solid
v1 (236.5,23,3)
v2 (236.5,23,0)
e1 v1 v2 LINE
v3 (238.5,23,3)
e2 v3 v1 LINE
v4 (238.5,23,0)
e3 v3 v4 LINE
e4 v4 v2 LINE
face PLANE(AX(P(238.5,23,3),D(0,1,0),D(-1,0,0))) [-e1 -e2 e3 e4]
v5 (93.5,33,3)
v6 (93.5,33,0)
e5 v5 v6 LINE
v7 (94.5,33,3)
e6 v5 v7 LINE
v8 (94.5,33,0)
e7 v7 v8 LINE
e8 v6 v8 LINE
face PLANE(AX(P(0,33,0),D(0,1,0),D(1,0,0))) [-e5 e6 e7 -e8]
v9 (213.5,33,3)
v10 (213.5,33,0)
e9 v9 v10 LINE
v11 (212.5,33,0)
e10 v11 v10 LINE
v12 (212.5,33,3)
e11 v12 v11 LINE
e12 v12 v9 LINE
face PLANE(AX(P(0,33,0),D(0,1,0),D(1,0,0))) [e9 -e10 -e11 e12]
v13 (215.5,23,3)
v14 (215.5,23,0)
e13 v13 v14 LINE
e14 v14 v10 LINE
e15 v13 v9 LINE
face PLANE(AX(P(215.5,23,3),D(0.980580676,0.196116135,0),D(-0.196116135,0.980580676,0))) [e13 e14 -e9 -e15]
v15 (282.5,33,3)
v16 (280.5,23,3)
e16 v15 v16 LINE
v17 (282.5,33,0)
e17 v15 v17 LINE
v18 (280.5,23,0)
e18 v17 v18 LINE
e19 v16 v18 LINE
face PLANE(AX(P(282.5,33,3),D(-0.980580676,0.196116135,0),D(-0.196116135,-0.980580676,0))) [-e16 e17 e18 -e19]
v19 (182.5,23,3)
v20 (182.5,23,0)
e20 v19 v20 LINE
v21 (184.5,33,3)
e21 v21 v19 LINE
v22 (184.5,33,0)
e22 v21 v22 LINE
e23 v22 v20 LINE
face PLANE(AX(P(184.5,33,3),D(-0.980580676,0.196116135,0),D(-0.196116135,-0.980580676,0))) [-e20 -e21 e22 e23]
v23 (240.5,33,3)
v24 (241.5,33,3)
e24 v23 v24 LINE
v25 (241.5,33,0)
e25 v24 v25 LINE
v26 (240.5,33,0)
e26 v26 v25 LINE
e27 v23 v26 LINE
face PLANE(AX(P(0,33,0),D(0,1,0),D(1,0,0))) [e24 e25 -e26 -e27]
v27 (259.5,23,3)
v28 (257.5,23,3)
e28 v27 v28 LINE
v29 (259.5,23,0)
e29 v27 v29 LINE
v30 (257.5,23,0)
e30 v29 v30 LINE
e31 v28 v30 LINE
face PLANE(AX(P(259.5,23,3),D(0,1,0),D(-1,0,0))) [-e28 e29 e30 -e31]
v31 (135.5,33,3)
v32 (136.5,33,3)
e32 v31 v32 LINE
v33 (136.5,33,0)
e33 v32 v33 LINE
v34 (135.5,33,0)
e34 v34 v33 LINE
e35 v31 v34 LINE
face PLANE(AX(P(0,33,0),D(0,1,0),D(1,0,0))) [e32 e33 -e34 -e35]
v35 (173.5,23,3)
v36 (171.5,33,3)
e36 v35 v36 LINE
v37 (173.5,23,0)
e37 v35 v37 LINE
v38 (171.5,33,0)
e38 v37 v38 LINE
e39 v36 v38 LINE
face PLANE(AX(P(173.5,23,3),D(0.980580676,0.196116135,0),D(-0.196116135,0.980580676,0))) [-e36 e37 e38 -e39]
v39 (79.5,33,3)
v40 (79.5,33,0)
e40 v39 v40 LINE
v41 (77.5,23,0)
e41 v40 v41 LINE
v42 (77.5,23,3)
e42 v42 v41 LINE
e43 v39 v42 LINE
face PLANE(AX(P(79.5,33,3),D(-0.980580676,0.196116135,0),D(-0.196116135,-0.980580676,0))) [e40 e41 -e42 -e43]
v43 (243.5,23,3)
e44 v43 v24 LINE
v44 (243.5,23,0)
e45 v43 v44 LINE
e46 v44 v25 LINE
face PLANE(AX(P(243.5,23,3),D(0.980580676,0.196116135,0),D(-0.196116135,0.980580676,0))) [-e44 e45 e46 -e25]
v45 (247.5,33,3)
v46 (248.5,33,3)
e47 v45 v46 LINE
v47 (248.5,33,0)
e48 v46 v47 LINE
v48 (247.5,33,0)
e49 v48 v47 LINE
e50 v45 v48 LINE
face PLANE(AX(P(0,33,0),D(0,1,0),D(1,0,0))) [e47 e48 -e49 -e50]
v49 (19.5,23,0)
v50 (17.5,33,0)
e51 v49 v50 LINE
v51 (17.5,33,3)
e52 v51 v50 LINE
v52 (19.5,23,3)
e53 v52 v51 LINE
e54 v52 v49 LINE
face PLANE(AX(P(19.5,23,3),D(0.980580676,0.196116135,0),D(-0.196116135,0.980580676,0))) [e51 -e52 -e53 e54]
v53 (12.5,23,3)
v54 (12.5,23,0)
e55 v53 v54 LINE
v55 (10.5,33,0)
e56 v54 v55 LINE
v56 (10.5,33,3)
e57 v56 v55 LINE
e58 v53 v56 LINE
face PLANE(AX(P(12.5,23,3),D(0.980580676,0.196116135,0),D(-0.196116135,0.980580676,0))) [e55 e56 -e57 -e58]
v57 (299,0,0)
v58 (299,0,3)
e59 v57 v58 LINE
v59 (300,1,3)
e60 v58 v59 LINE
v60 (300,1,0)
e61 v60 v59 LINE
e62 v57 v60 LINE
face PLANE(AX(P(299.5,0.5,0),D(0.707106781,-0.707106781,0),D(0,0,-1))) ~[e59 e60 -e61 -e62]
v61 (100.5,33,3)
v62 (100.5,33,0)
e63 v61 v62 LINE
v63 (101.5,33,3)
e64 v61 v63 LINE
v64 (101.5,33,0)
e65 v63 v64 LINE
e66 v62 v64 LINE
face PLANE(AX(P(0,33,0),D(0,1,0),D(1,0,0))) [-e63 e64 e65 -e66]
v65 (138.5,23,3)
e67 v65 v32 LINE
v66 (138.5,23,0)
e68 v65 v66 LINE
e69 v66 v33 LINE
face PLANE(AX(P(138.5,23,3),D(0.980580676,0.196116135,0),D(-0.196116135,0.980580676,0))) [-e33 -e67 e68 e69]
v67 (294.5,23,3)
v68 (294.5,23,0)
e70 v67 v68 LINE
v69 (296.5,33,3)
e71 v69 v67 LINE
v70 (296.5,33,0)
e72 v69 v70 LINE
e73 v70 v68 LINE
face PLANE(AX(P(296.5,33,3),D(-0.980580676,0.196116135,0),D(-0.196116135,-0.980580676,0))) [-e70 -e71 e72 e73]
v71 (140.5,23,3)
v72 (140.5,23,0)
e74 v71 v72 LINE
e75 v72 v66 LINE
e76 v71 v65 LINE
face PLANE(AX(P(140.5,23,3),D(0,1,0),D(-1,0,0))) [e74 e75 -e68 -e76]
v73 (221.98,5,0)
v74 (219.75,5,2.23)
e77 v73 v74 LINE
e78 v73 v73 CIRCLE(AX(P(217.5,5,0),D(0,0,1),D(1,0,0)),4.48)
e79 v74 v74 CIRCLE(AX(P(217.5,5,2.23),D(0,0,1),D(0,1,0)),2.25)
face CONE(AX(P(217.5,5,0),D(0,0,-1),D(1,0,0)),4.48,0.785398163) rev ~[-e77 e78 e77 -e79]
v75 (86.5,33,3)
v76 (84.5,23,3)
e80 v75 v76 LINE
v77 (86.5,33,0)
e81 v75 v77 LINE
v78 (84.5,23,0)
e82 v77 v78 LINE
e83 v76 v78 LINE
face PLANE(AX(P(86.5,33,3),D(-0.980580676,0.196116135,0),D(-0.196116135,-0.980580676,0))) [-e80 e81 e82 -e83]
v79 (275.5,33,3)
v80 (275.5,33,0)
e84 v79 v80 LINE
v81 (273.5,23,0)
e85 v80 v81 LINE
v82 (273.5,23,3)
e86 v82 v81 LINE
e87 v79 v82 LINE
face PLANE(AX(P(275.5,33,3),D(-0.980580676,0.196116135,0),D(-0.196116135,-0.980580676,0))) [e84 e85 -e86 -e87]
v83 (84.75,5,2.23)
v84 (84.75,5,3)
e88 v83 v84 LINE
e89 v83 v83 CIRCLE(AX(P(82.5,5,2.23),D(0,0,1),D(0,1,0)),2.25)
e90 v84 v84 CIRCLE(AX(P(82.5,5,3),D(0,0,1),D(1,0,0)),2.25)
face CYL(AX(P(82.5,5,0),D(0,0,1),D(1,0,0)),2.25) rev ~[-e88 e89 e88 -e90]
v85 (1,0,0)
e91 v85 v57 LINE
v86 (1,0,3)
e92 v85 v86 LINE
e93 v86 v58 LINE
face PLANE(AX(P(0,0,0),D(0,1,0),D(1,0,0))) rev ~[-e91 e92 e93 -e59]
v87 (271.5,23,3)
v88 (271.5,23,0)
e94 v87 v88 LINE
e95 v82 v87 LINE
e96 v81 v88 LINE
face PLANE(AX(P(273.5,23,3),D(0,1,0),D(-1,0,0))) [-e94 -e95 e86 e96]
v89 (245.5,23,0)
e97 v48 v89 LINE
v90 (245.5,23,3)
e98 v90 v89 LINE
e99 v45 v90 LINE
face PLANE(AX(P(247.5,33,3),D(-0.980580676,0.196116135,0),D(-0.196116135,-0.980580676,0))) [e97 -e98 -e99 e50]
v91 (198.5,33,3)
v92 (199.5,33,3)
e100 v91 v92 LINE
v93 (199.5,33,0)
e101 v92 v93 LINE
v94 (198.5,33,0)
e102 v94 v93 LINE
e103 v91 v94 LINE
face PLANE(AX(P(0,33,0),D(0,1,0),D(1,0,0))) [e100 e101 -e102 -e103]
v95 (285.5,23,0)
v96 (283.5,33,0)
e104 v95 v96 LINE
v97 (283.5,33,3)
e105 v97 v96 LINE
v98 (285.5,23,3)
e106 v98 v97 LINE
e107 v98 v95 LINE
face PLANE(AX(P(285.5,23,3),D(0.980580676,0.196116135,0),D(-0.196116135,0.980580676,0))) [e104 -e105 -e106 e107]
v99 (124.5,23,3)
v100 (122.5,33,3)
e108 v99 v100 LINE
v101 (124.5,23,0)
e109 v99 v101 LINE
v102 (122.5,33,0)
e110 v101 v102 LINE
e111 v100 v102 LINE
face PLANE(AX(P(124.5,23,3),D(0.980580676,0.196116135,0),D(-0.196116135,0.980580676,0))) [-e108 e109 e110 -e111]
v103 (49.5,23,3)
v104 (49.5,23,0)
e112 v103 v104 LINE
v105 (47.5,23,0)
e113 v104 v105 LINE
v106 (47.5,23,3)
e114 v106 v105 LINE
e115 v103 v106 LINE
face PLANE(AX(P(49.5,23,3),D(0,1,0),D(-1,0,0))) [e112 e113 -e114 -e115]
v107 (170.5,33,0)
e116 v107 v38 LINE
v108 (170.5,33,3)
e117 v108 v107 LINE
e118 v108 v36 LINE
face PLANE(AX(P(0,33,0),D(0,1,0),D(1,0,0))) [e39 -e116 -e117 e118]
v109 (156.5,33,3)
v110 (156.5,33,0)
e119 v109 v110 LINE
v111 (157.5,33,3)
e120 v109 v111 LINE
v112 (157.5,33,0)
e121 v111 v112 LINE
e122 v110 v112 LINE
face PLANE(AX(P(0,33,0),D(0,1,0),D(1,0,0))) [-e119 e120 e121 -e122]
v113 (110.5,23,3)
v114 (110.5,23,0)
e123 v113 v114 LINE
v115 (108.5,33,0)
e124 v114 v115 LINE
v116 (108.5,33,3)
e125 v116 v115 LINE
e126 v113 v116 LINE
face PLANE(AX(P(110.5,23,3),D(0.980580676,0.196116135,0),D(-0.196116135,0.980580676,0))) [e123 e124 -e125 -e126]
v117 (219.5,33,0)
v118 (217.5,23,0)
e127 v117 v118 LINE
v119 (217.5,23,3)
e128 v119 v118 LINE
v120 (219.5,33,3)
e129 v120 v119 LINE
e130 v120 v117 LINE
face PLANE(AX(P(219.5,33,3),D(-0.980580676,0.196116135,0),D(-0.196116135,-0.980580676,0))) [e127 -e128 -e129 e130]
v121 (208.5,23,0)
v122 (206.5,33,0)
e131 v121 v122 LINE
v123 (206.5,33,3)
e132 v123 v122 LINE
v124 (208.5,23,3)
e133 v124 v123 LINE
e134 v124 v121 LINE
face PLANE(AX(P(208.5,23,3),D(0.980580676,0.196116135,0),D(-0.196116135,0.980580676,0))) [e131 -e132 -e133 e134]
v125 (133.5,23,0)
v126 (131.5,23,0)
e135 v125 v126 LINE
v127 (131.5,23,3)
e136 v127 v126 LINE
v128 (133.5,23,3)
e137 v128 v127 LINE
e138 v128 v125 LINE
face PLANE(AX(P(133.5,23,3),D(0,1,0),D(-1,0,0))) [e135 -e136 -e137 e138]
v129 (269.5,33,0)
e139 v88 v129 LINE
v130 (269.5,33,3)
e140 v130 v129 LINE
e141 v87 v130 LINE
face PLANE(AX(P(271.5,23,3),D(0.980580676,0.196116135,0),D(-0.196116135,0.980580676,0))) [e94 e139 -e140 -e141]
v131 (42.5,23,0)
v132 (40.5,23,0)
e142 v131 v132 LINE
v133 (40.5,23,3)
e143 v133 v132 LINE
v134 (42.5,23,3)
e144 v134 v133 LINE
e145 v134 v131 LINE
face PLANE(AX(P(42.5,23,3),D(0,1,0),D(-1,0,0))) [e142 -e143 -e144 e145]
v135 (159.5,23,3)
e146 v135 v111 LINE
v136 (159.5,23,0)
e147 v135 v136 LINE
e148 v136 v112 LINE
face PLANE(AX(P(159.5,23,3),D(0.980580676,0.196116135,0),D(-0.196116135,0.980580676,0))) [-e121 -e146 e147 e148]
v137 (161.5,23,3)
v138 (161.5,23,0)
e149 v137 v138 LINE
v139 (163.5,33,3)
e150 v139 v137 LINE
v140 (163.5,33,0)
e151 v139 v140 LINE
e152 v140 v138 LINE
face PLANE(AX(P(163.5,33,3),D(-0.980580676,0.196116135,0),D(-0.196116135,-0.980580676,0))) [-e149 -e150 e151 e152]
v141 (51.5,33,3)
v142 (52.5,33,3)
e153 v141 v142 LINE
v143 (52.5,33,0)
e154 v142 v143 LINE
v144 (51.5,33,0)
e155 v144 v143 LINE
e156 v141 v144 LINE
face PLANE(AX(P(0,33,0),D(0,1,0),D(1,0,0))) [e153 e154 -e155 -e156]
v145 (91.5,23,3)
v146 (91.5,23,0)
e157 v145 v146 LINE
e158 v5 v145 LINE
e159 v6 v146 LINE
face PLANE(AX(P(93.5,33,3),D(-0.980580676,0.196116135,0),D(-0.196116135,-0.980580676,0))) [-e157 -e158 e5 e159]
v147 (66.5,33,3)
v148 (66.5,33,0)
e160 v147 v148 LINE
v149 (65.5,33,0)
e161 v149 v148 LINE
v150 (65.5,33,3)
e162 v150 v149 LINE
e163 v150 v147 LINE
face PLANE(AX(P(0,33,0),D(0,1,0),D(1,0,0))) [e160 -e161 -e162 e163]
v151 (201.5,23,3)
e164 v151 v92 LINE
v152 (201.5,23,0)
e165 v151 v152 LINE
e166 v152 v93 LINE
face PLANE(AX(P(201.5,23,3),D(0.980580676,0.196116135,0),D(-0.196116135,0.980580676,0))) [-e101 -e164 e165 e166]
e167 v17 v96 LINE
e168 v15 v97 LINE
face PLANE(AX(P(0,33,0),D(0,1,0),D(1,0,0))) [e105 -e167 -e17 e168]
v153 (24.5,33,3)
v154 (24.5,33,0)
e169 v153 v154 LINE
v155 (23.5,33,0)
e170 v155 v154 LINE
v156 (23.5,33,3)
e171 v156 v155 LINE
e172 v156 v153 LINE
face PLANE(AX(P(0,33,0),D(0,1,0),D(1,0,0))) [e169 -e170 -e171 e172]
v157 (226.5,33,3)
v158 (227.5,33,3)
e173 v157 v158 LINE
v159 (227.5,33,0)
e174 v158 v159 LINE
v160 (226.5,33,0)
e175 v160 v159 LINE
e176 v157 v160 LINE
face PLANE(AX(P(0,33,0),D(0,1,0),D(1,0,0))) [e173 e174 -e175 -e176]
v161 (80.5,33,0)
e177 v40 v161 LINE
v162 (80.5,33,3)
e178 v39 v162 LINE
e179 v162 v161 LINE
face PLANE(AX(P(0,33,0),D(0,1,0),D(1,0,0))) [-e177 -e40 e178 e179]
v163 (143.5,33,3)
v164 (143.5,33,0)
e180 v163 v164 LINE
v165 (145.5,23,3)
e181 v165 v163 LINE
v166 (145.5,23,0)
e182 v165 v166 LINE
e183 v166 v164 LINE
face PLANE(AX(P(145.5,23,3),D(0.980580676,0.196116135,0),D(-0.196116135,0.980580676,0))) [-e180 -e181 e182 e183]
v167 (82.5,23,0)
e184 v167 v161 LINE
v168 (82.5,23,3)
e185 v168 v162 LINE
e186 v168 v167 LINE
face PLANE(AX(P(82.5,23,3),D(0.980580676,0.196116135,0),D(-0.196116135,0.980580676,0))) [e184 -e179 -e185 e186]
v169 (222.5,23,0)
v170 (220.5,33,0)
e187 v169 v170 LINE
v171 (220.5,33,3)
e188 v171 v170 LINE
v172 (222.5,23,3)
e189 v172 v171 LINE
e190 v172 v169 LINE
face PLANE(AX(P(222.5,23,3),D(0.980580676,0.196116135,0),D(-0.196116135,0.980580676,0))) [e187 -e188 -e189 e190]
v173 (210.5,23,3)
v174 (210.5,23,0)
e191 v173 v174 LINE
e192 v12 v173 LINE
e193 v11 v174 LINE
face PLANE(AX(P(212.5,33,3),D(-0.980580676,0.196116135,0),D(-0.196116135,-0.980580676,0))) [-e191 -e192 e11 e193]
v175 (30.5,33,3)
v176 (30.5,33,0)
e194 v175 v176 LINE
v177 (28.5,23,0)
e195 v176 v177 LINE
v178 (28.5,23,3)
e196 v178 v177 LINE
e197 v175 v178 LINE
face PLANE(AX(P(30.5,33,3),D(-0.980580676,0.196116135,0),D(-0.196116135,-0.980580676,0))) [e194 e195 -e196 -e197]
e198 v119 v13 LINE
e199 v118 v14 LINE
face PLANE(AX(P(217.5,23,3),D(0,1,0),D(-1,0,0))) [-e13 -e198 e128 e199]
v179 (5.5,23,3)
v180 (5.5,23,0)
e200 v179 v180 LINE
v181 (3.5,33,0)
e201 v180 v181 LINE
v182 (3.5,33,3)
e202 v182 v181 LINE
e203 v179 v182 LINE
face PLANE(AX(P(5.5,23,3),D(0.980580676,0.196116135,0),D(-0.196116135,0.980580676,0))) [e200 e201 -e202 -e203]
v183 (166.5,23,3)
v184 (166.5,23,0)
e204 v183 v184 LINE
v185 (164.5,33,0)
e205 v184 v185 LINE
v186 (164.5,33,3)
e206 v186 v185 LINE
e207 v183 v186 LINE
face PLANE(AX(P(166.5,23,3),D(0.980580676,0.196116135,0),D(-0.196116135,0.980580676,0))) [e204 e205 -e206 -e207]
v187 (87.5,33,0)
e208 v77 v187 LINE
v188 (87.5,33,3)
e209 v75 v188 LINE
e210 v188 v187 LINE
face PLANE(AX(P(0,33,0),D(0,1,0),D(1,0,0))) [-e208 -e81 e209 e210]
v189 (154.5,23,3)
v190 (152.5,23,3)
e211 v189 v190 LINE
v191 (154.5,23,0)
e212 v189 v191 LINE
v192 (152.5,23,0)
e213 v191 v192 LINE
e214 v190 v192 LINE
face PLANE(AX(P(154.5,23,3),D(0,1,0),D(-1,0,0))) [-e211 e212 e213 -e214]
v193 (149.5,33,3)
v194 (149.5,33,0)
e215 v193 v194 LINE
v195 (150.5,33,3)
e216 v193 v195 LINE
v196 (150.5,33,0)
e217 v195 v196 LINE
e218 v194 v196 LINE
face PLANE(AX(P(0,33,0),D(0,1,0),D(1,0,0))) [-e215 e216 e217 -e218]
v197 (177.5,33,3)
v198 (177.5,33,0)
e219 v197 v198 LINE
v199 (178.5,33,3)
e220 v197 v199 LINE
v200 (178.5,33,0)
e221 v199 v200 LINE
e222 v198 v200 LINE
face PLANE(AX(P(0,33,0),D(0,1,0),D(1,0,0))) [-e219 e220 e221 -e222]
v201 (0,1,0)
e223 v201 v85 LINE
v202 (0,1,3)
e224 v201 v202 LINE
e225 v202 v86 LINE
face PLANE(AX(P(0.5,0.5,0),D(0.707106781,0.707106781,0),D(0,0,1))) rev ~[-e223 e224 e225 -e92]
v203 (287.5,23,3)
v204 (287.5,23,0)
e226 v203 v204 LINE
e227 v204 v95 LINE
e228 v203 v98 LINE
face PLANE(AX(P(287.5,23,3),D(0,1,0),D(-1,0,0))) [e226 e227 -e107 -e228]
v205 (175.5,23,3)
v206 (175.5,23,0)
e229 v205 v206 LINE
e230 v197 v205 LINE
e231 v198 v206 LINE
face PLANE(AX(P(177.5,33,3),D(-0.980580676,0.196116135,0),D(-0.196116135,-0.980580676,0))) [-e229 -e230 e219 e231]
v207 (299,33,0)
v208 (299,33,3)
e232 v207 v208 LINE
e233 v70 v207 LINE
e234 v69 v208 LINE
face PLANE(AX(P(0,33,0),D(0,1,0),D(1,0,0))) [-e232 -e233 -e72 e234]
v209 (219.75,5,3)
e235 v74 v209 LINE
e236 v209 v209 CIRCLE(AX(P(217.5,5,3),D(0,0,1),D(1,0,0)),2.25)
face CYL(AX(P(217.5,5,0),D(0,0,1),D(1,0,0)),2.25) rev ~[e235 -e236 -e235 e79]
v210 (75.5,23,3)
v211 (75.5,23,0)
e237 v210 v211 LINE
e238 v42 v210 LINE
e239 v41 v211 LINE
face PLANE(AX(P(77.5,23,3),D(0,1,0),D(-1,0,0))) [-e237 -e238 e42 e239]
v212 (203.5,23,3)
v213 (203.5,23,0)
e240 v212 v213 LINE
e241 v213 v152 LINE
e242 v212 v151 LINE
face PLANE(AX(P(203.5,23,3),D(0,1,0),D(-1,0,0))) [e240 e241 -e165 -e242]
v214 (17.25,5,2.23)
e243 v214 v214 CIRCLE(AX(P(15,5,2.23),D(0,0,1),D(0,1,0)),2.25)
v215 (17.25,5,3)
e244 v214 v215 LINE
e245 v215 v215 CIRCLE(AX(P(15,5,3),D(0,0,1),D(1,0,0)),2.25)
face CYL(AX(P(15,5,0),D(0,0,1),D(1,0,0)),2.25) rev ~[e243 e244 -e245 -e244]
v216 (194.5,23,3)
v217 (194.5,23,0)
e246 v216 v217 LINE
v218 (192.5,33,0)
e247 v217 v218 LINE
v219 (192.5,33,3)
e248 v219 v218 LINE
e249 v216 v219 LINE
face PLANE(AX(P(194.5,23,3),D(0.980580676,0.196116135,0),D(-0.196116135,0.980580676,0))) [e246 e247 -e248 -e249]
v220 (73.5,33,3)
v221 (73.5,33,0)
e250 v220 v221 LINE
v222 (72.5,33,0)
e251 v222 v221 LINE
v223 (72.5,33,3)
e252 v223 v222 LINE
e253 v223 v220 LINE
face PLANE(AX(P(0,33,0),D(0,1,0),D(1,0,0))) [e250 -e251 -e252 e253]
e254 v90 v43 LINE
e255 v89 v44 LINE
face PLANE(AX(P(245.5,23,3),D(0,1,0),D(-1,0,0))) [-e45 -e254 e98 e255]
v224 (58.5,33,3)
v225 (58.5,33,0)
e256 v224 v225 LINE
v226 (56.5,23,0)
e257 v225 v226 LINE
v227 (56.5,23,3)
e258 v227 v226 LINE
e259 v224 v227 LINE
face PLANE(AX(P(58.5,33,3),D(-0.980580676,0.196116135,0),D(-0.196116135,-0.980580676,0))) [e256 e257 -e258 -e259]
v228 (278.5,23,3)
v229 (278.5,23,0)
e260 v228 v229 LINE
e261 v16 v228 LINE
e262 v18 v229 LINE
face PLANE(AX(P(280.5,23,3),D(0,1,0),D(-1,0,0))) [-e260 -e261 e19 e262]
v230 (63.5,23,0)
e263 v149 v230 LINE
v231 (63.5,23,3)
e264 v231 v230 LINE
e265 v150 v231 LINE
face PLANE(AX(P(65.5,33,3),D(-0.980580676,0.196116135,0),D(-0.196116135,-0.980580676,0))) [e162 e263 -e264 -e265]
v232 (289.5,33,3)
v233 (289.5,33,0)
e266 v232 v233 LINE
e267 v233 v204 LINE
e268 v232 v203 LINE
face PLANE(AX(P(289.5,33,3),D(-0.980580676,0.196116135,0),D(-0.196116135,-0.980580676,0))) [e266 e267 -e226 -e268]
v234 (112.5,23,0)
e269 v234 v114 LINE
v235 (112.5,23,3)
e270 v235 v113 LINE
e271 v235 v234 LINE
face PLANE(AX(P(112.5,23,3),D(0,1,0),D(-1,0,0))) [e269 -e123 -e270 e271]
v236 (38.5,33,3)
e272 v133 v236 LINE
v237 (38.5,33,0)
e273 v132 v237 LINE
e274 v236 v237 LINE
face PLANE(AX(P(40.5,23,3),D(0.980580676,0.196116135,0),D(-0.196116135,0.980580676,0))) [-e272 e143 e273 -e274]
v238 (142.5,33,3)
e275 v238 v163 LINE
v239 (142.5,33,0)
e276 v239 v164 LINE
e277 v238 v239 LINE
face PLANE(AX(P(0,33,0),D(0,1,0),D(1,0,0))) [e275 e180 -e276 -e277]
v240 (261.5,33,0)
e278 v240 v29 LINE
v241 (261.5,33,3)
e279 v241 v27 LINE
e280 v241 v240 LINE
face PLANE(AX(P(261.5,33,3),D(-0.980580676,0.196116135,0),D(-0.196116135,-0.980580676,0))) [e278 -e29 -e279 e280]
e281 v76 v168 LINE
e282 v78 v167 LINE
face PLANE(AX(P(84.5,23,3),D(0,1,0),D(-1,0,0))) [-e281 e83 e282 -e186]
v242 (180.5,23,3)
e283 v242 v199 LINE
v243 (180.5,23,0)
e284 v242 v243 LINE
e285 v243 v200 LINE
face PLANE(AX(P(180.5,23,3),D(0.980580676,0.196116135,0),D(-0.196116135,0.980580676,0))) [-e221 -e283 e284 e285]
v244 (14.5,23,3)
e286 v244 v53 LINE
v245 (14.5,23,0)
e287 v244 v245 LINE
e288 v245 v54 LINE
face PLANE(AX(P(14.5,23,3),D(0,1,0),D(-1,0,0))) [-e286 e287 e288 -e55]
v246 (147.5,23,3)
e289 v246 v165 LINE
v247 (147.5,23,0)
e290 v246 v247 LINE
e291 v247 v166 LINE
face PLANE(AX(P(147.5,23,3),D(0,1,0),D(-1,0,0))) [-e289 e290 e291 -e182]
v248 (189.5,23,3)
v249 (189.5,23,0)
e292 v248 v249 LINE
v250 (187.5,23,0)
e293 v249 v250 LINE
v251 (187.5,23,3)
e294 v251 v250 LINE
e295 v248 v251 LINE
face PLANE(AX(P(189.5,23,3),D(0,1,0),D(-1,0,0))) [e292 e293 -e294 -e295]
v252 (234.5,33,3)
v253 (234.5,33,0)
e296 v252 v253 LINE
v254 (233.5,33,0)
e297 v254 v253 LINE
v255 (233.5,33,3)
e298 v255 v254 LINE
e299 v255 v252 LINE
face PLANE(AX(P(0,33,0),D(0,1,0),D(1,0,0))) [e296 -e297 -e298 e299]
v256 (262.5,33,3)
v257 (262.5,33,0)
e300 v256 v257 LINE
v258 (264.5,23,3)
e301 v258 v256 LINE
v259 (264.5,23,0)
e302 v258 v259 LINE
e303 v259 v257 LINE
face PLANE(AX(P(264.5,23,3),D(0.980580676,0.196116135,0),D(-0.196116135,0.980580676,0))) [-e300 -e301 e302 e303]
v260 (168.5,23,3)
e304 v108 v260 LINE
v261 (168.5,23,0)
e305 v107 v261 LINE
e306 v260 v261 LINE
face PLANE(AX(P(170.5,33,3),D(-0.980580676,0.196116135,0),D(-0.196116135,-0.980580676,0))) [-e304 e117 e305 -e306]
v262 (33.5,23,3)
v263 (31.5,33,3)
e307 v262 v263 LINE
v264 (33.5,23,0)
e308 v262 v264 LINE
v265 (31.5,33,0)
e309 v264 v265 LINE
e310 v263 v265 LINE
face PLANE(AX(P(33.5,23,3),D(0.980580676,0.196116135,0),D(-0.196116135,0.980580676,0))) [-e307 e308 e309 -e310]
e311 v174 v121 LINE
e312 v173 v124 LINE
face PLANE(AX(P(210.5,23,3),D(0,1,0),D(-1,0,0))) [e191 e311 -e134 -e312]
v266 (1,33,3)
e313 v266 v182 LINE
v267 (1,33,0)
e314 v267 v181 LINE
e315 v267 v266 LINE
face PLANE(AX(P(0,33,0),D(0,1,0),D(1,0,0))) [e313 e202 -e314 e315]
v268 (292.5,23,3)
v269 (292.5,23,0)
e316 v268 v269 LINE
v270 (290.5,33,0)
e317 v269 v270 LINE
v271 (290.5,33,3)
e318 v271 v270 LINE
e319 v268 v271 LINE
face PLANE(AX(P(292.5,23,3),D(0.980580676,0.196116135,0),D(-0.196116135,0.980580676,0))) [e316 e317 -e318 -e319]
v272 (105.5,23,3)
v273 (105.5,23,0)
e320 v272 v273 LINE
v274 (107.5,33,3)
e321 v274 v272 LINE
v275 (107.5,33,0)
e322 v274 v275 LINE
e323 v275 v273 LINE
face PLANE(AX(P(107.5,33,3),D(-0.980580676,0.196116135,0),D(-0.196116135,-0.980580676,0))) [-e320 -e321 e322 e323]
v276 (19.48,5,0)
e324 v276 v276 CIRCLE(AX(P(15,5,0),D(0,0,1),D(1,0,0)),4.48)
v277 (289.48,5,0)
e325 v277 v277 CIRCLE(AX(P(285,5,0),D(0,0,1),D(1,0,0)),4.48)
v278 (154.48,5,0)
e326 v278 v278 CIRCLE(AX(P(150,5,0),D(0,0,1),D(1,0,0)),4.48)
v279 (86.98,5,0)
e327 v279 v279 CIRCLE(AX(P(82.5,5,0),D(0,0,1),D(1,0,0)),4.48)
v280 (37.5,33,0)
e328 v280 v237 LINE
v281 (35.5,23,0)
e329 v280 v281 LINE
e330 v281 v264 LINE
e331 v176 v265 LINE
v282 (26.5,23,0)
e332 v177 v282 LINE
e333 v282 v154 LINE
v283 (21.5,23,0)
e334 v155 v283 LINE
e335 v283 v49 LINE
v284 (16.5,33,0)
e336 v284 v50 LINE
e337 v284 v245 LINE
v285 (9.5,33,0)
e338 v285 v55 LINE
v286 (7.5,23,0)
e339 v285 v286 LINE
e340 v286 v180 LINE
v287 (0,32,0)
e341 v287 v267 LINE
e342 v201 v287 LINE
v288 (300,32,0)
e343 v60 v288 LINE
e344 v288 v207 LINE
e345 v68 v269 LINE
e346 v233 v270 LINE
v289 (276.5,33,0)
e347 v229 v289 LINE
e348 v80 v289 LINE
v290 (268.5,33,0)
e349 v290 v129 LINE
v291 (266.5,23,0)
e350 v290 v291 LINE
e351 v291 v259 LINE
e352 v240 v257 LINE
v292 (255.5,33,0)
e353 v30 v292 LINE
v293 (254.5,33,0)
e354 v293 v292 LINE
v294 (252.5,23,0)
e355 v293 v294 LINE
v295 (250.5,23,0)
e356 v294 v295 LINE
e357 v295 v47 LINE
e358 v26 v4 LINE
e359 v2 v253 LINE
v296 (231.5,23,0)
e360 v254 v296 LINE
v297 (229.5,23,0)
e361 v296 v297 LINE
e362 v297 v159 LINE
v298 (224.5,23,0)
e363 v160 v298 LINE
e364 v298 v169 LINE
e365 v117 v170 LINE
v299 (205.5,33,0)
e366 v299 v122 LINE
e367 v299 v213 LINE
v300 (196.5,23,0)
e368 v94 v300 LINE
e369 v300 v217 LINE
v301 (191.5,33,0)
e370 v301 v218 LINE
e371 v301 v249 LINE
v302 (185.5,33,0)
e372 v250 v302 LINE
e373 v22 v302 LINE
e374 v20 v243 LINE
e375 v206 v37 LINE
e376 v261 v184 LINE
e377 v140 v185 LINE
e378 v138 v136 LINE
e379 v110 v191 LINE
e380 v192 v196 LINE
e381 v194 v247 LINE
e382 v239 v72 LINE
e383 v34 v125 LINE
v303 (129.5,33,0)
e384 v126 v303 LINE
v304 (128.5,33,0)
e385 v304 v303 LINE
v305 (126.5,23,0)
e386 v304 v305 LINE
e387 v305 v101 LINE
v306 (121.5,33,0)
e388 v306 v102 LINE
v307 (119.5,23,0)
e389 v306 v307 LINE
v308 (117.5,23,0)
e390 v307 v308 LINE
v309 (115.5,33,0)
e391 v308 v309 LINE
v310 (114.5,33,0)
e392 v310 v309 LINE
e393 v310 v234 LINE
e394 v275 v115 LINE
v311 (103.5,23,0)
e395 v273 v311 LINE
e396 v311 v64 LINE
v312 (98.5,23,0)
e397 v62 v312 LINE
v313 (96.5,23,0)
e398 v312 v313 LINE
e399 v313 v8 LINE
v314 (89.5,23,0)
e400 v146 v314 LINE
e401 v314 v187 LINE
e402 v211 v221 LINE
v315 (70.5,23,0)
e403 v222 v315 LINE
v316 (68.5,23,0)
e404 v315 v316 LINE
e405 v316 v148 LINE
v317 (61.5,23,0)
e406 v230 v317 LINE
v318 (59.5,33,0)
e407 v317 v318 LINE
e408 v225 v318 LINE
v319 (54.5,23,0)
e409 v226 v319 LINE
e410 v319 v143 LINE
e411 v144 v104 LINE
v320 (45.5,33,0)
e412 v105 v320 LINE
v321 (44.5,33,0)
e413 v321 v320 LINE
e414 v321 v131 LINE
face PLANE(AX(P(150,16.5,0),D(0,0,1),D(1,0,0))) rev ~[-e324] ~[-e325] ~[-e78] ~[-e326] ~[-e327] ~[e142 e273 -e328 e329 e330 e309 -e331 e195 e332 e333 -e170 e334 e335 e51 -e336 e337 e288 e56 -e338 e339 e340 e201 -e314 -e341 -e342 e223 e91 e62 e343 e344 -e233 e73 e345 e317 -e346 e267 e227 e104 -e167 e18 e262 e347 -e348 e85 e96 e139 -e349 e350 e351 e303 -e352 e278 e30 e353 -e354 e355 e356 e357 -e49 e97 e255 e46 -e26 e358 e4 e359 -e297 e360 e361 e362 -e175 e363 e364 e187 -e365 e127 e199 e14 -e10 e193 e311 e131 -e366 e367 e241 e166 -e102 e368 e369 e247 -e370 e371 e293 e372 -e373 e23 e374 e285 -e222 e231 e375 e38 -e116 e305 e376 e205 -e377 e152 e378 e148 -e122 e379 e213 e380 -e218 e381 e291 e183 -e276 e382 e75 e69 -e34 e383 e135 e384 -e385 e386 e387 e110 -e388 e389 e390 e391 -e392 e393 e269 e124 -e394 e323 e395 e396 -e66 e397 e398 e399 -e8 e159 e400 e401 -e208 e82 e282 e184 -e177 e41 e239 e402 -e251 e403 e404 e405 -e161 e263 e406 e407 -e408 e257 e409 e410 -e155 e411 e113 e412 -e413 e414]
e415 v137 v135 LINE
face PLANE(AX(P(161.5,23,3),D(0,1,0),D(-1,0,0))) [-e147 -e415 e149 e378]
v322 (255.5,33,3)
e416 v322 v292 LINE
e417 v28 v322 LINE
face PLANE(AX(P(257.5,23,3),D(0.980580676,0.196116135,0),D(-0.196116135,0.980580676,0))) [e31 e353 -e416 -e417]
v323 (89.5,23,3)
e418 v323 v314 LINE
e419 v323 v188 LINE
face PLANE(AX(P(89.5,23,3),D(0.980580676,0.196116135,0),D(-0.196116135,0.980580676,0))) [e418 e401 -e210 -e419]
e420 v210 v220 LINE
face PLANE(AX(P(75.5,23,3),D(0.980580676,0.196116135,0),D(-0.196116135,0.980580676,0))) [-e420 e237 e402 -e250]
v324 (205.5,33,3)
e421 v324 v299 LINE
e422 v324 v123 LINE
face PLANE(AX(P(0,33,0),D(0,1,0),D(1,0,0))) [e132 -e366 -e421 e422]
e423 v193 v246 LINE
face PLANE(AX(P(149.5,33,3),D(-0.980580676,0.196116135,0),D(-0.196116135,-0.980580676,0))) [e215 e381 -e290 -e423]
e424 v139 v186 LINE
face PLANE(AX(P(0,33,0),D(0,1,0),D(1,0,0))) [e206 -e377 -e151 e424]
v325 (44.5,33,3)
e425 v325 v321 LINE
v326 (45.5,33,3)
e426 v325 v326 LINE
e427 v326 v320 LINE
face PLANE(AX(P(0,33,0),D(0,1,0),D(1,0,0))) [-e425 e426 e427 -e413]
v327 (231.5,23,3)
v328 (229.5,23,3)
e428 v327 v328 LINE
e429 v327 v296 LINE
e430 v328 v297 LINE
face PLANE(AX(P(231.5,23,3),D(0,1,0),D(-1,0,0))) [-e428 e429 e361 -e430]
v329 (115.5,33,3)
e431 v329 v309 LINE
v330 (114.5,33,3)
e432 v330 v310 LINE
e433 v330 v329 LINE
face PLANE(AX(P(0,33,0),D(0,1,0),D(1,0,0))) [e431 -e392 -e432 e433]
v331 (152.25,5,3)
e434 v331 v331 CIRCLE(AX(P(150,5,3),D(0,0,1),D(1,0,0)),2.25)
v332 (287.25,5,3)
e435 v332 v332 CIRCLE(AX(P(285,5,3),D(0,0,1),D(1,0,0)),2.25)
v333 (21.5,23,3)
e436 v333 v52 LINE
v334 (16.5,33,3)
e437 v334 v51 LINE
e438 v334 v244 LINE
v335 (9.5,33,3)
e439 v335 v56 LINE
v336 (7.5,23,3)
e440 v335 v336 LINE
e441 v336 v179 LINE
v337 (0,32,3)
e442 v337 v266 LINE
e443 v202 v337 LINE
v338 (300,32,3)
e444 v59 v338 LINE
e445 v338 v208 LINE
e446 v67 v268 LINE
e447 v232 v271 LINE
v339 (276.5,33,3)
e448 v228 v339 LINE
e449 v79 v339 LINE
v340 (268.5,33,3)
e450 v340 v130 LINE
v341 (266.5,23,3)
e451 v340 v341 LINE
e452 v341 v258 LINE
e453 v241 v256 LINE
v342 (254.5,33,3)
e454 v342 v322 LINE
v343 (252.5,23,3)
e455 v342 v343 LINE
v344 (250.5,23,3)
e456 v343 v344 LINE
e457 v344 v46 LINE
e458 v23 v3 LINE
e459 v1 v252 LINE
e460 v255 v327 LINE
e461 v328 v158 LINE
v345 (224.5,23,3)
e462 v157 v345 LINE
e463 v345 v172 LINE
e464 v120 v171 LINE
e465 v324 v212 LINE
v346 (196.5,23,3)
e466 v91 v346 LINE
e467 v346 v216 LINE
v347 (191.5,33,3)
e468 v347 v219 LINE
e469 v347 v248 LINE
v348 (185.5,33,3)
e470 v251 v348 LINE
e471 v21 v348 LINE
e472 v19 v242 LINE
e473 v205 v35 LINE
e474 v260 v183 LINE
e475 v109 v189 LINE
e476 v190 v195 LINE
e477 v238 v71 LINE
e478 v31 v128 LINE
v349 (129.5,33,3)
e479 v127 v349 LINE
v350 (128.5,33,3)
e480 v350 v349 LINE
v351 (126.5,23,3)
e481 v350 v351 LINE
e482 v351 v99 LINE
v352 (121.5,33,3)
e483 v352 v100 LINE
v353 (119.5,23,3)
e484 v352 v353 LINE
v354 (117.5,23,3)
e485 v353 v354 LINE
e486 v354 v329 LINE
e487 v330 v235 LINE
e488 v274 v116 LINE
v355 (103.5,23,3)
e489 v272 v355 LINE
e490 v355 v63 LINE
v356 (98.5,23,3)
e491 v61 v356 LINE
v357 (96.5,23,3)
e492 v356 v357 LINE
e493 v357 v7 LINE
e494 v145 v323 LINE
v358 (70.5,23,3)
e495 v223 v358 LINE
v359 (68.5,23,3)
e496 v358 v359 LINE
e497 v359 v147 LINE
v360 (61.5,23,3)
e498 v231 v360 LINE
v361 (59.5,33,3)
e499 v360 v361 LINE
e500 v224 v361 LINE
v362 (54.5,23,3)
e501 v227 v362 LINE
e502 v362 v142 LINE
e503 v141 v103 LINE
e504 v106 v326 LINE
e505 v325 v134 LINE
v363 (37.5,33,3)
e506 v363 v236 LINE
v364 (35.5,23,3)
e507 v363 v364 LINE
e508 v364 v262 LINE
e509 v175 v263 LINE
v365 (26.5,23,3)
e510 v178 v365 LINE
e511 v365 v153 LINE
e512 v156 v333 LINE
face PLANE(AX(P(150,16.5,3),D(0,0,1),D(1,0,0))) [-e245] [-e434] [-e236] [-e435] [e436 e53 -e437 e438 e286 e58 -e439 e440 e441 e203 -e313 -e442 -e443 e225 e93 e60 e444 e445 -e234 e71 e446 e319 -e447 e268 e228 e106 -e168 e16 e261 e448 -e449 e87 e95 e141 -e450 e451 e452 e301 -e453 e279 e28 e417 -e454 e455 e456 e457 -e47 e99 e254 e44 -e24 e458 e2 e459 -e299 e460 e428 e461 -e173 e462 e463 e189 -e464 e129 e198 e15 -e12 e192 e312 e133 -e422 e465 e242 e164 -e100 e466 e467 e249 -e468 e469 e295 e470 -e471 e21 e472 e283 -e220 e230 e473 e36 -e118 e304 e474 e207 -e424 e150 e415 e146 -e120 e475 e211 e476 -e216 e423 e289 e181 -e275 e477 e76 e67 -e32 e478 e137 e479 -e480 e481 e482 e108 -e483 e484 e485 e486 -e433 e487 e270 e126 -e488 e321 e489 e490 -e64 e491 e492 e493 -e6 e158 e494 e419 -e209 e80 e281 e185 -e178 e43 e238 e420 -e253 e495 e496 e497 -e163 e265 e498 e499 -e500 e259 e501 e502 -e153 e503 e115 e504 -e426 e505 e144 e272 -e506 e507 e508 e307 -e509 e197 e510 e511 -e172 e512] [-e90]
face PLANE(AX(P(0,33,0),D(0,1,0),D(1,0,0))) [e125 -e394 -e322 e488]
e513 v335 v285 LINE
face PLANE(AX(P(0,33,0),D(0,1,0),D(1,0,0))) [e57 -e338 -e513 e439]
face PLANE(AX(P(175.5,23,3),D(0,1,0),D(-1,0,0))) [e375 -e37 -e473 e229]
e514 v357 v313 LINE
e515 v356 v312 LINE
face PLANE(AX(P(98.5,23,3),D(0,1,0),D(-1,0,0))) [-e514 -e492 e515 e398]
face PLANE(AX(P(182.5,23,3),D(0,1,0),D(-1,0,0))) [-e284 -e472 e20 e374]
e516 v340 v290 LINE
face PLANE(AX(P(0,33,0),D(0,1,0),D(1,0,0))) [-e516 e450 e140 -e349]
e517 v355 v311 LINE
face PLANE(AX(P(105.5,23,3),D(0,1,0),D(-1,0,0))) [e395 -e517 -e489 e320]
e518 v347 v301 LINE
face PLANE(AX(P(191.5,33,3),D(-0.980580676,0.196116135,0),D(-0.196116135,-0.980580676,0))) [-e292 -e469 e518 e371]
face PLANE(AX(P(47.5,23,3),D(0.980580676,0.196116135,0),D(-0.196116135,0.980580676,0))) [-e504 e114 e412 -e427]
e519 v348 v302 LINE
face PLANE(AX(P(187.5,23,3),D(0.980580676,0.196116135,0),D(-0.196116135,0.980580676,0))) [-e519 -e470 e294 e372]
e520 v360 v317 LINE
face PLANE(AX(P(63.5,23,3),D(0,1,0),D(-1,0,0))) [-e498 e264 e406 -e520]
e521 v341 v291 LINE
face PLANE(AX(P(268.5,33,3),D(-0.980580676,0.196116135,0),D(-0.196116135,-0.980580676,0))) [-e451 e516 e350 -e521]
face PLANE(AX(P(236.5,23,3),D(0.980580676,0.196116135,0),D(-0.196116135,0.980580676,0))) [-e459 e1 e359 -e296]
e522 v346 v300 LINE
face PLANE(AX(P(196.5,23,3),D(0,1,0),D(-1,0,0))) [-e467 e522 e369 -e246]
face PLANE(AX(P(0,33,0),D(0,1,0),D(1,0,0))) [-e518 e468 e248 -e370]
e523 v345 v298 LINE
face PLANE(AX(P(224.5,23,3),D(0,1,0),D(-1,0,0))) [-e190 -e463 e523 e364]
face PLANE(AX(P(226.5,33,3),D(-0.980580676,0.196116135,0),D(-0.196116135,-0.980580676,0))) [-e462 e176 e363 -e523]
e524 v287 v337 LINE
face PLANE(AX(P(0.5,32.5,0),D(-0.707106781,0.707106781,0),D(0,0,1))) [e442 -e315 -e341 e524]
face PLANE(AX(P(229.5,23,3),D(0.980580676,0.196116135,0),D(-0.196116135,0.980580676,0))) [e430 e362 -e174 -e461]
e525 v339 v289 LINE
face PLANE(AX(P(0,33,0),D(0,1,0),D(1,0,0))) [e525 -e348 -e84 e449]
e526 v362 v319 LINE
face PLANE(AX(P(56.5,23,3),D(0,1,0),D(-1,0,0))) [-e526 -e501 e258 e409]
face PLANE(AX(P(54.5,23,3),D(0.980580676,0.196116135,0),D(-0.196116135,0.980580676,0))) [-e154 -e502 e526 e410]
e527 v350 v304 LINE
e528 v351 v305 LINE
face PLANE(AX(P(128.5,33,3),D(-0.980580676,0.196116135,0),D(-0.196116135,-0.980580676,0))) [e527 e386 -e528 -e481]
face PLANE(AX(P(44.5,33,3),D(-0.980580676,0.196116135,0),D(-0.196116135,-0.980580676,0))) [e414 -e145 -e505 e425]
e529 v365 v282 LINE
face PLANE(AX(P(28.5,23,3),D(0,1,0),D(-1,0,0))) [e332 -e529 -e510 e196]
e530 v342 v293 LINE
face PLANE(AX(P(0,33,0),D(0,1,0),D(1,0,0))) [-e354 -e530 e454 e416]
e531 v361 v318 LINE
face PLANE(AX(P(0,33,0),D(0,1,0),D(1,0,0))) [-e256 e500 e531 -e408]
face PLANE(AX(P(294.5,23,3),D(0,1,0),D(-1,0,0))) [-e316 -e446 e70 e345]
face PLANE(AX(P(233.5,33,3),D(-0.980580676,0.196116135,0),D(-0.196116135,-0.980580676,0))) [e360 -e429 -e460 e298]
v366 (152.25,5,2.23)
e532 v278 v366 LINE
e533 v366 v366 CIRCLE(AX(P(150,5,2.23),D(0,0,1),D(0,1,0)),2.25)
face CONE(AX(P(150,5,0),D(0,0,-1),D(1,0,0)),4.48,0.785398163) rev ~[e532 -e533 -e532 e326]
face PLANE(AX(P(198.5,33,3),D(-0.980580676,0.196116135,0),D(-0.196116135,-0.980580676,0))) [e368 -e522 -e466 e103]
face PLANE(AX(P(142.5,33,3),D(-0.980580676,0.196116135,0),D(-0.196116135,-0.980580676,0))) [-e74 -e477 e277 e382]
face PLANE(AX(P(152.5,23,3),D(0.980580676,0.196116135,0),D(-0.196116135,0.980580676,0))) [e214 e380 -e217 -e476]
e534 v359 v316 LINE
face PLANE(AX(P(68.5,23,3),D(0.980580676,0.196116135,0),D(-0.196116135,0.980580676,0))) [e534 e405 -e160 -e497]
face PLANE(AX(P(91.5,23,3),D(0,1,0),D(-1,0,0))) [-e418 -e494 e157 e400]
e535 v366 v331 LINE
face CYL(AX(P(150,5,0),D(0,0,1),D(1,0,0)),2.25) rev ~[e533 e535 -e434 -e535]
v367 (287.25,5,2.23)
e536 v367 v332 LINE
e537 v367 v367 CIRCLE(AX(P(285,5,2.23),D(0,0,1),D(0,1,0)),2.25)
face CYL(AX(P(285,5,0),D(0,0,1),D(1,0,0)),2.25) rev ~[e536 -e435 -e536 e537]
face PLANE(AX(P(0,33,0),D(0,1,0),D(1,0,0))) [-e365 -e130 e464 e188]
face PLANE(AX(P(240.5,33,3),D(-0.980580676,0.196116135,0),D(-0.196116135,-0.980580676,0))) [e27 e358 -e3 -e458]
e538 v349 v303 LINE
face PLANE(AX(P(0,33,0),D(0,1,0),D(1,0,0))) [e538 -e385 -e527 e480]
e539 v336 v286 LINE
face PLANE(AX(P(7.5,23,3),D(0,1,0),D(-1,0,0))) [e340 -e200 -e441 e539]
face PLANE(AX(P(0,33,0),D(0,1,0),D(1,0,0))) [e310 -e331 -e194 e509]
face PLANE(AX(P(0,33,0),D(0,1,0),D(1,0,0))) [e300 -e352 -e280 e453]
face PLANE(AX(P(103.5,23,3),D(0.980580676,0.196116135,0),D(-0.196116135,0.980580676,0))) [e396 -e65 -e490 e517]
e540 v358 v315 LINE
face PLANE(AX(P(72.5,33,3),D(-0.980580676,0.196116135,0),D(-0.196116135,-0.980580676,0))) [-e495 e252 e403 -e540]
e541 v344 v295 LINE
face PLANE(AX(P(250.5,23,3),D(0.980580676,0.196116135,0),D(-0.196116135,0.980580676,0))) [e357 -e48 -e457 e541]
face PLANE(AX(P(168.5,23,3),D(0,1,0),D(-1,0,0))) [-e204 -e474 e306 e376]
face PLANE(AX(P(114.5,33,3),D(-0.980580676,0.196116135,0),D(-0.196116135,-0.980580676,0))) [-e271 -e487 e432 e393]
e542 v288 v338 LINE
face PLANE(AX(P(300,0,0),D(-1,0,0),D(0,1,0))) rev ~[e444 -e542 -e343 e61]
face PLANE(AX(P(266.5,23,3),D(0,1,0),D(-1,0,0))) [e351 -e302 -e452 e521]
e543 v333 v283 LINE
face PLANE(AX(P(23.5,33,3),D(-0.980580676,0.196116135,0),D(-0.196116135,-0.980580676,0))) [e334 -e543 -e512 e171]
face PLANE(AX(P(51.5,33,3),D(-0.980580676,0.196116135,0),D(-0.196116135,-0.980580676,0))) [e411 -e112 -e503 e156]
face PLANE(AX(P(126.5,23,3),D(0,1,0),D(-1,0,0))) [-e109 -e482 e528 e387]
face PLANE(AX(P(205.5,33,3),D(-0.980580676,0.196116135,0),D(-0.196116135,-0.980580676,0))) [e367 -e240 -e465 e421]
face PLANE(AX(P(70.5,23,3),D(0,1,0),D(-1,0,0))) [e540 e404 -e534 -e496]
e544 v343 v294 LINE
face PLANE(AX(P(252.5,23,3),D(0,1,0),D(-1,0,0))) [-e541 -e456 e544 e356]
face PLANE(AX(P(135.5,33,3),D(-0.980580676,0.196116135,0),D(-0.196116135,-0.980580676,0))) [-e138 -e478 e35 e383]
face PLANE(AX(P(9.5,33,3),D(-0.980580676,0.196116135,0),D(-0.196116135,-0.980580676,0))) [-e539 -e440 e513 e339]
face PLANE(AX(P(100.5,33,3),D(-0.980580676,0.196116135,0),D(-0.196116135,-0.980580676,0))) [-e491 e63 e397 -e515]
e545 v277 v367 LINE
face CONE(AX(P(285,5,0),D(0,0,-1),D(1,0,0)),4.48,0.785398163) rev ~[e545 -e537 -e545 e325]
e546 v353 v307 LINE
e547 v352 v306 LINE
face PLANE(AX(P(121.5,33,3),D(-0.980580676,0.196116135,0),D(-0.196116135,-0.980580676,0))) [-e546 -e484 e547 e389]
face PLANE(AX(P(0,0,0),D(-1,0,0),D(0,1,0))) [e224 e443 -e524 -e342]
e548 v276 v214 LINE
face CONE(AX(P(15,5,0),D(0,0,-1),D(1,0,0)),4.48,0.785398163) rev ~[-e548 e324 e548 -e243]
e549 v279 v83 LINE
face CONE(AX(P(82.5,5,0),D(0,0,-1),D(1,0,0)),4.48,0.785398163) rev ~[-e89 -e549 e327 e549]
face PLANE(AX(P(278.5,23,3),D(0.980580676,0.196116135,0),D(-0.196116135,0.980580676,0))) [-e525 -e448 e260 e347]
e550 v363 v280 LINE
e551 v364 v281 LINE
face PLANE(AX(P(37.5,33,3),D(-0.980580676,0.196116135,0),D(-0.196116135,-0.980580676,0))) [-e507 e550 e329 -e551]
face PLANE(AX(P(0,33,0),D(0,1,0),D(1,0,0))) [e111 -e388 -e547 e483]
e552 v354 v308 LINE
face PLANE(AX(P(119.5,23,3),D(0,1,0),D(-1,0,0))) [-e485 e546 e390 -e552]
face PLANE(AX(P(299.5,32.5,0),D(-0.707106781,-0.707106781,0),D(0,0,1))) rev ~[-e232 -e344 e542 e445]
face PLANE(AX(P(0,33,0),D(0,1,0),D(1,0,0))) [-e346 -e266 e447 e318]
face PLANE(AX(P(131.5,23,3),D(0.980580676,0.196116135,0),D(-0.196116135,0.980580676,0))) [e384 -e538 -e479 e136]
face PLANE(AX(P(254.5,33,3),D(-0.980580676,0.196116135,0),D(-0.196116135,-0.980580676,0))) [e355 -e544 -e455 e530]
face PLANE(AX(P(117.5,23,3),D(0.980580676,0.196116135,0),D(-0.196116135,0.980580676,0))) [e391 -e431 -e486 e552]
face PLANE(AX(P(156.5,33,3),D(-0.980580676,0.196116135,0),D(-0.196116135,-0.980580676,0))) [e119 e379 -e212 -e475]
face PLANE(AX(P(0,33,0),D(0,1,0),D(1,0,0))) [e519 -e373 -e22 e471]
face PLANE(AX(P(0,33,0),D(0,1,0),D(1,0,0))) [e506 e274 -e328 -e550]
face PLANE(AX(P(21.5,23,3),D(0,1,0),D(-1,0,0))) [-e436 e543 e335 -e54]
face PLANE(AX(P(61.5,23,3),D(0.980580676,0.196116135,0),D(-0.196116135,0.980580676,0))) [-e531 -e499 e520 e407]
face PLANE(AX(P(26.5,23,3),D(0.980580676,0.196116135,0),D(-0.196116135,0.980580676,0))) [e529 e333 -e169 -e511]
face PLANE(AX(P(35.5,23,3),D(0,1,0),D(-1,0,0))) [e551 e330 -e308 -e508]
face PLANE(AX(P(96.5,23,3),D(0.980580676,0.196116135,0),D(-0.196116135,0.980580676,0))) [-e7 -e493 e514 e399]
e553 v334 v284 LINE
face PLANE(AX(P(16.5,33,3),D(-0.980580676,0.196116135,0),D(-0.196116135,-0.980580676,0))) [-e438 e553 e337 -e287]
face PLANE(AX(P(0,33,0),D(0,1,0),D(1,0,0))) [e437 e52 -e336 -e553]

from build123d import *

# Parameters (mm, degrees)
SKETCH_2_W                   = 300
SKETCH_2_H                   = 33
EXTRUDE_1_DEPTH              = 3
CUT_EXTRUDE_1_DEPTH          = 15
CHAMFER_1_SIZE               = 1
HOLE_WIZARD_M4_1_D           = 4.5
HOLE_WIZARD_M4_1_DEPTH       = 11.5
HOLE_WIZARD_M4_1_CSINK_D     = 8.96
HOLE_WIZARD_M4_1_CSINK_ANGLE = 90
HOLE_WIZARD_M4_1_TIP         = 1.351936393


with BuildPart() as part:
    # 草图2 → 凸台-拉伸1 (new body)
    with BuildSketch(Plane.XY):
        with Locations((150, 16.5)):
            Rectangle(SKETCH_2_W, SKETCH_2_H)
    extrude(amount=EXTRUDE_1_DEPTH)

    # 草图3 → 切除-拉伸1 (cut)
    with BuildSketch(Plane.XY.offset(3)):
        Polygon((3.5, 33), (9.5, 33), (7.5, 23), (5.5, 23), align=None)
        Polygon((12.5, 23), (10.5, 33), (16.5, 33), (14.5, 23), align=None)
        Polygon((19.5, 23), (17.5, 33), (23.5, 33), (21.5, 23), align=None)
        Polygon((26.5, 23), (24.5, 33), (30.5, 33), (28.5, 23), align=None)
        Polygon((33.5, 23), (31.5, 33), (37.5, 33), (35.5, 23), align=None)
        Polygon((40.5, 23), (38.5, 33), (44.5, 33), (42.5, 23), align=None)
        Polygon((47.5, 23), (45.5, 33), (51.5, 33), (49.5, 23), align=None)
        Polygon((54.5, 23), (52.5, 33), (58.5, 33), (56.5, 23), align=None)
        Polygon((61.5, 23), (59.5, 33), (65.5, 33), (63.5, 23), align=None)
        Polygon((68.5, 23), (66.5, 33), (72.5, 33), (70.5, 23), align=None)
        Polygon((75.5, 23), (73.5, 33), (79.5, 33), (77.5, 23), align=None)
        Polygon((82.5, 23), (80.5, 33), (86.5, 33), (84.5, 23), align=None)
        Polygon((89.5, 23), (87.5, 33), (93.5, 33), (91.5, 23), align=None)
        Polygon((96.5, 23), (94.5, 33), (100.5, 33), (98.5, 23), align=None)
        Polygon((103.5, 23), (101.5, 33), (107.5, 33), (105.5, 23), align=None)
        Polygon((110.5, 23), (108.5, 33), (114.5, 33), (112.5, 23), align=None)
        Polygon((117.5, 23), (115.5, 33), (121.5, 33), (119.5, 23), align=None)
        Polygon((124.5, 23), (122.5, 33), (128.5, 33), (126.5, 23), align=None)
        Polygon((131.5, 23), (129.5, 33), (135.5, 33), (133.5, 23), align=None)
        Polygon((138.5, 23), (136.5, 33), (142.5, 33), (140.5, 23), align=None)
        Polygon((145.5, 23), (143.5, 33), (149.5, 33), (147.5, 23), align=None)
        Polygon((152.5, 23), (150.5, 33), (156.5, 33), (154.5, 23), align=None)
        Polygon((159.5, 23), (157.5, 33), (163.5, 33), (161.5, 23), align=None)
        Polygon((166.5, 23), (164.5, 33), (170.5, 33), (168.5, 23), align=None)
        Polygon((173.5, 23), (171.5, 33), (177.5, 33), (175.5, 23), align=None)
        Polygon((180.5, 23), (178.5, 33), (184.5, 33), (182.5, 23), align=None)
        Polygon((187.5, 23), (185.5, 33), (191.5, 33), (189.5, 23), align=None)
        Polygon((194.5, 23), (192.5, 33), (198.5, 33), (196.5, 23), align=None)
        Polygon((201.5, 23), (199.5, 33), (205.5, 33), (203.5, 23), align=None)
        Polygon((208.5, 23), (206.5, 33), (212.5, 33), (210.5, 23), align=None)
        Polygon((215.5, 23), (213.5, 33), (219.5, 33), (217.5, 23), align=None)
        Polygon((222.5, 23), (220.5, 33), (226.5, 33), (224.5, 23), align=None)
        Polygon((229.5, 23), (227.5, 33), (233.5, 33), (231.5, 23), align=None)
        Polygon((236.5, 23), (234.5, 33), (240.5, 33), (238.5, 23), align=None)
        Polygon((243.5, 23), (241.5, 33), (247.5, 33), (245.5, 23), align=None)
        Polygon((250.5, 23), (248.5, 33), (254.5, 33), (252.5, 23), align=None)
        Polygon((257.5, 23), (255.5, 33), (261.5, 33), (259.5, 23), align=None)
        Polygon((264.5, 23), (262.5, 33), (268.5, 33), (266.5, 23), align=None)
        Polygon((271.5, 23), (269.5, 33), (275.5, 33), (273.5, 23), align=None)
        Polygon((278.5, 23), (276.5, 33), (282.5, 33), (280.5, 23), align=None)
        Polygon((285.5, 23), (283.5, 33), (289.5, 33), (287.5, 23), align=None)
        Polygon((292.5, 23), (290.5, 33), (296.5, 33), (294.5, 23), align=None)
    extrude(amount=-CUT_EXTRUDE_1_DEPTH, mode=Mode.SUBTRACT)

    # 倒角1
    chamfer_1_edges = [part.edges().sort_by_distance(p)[0] for p in [
        (0, 33, 1.5),
        (300, 33, 1.5),
        (300, 0, 1.5),
        (0, 0, 1.5),
    ]]
    chamfer(chamfer_1_edges, length=CHAMFER_1_SIZE)

    # M4 六角凹锥坑螺钉的锥形沉头孔1
    with Locations(Plane(origin=(0, 0, 0), x_dir=(-1, 0, 0), z_dir=(0, 0, -1))):
        with Locations((-285, 5), (-217.5, 5), (-150, 5), (-82.5, 5), (-15, 5)):
            CounterSinkHole(HOLE_WIZARD_M4_1_D / 2, HOLE_WIZARD_M4_1_CSINK_D / 2, depth=HOLE_WIZARD_M4_1_DEPTH, counter_sink_angle=HOLE_WIZARD_M4_1_CSINK_ANGLE)
            with Locations((0, 0, -(HOLE_WIZARD_M4_1_DEPTH + HOLE_WIZARD_M4_1_TIP / 2))):  # 118° drill point
                Cone(0, HOLE_WIZARD_M4_1_D / 2, HOLE_WIZARD_M4_1_TIP, mode=Mode.SUBTRACT)


solid = part.part
